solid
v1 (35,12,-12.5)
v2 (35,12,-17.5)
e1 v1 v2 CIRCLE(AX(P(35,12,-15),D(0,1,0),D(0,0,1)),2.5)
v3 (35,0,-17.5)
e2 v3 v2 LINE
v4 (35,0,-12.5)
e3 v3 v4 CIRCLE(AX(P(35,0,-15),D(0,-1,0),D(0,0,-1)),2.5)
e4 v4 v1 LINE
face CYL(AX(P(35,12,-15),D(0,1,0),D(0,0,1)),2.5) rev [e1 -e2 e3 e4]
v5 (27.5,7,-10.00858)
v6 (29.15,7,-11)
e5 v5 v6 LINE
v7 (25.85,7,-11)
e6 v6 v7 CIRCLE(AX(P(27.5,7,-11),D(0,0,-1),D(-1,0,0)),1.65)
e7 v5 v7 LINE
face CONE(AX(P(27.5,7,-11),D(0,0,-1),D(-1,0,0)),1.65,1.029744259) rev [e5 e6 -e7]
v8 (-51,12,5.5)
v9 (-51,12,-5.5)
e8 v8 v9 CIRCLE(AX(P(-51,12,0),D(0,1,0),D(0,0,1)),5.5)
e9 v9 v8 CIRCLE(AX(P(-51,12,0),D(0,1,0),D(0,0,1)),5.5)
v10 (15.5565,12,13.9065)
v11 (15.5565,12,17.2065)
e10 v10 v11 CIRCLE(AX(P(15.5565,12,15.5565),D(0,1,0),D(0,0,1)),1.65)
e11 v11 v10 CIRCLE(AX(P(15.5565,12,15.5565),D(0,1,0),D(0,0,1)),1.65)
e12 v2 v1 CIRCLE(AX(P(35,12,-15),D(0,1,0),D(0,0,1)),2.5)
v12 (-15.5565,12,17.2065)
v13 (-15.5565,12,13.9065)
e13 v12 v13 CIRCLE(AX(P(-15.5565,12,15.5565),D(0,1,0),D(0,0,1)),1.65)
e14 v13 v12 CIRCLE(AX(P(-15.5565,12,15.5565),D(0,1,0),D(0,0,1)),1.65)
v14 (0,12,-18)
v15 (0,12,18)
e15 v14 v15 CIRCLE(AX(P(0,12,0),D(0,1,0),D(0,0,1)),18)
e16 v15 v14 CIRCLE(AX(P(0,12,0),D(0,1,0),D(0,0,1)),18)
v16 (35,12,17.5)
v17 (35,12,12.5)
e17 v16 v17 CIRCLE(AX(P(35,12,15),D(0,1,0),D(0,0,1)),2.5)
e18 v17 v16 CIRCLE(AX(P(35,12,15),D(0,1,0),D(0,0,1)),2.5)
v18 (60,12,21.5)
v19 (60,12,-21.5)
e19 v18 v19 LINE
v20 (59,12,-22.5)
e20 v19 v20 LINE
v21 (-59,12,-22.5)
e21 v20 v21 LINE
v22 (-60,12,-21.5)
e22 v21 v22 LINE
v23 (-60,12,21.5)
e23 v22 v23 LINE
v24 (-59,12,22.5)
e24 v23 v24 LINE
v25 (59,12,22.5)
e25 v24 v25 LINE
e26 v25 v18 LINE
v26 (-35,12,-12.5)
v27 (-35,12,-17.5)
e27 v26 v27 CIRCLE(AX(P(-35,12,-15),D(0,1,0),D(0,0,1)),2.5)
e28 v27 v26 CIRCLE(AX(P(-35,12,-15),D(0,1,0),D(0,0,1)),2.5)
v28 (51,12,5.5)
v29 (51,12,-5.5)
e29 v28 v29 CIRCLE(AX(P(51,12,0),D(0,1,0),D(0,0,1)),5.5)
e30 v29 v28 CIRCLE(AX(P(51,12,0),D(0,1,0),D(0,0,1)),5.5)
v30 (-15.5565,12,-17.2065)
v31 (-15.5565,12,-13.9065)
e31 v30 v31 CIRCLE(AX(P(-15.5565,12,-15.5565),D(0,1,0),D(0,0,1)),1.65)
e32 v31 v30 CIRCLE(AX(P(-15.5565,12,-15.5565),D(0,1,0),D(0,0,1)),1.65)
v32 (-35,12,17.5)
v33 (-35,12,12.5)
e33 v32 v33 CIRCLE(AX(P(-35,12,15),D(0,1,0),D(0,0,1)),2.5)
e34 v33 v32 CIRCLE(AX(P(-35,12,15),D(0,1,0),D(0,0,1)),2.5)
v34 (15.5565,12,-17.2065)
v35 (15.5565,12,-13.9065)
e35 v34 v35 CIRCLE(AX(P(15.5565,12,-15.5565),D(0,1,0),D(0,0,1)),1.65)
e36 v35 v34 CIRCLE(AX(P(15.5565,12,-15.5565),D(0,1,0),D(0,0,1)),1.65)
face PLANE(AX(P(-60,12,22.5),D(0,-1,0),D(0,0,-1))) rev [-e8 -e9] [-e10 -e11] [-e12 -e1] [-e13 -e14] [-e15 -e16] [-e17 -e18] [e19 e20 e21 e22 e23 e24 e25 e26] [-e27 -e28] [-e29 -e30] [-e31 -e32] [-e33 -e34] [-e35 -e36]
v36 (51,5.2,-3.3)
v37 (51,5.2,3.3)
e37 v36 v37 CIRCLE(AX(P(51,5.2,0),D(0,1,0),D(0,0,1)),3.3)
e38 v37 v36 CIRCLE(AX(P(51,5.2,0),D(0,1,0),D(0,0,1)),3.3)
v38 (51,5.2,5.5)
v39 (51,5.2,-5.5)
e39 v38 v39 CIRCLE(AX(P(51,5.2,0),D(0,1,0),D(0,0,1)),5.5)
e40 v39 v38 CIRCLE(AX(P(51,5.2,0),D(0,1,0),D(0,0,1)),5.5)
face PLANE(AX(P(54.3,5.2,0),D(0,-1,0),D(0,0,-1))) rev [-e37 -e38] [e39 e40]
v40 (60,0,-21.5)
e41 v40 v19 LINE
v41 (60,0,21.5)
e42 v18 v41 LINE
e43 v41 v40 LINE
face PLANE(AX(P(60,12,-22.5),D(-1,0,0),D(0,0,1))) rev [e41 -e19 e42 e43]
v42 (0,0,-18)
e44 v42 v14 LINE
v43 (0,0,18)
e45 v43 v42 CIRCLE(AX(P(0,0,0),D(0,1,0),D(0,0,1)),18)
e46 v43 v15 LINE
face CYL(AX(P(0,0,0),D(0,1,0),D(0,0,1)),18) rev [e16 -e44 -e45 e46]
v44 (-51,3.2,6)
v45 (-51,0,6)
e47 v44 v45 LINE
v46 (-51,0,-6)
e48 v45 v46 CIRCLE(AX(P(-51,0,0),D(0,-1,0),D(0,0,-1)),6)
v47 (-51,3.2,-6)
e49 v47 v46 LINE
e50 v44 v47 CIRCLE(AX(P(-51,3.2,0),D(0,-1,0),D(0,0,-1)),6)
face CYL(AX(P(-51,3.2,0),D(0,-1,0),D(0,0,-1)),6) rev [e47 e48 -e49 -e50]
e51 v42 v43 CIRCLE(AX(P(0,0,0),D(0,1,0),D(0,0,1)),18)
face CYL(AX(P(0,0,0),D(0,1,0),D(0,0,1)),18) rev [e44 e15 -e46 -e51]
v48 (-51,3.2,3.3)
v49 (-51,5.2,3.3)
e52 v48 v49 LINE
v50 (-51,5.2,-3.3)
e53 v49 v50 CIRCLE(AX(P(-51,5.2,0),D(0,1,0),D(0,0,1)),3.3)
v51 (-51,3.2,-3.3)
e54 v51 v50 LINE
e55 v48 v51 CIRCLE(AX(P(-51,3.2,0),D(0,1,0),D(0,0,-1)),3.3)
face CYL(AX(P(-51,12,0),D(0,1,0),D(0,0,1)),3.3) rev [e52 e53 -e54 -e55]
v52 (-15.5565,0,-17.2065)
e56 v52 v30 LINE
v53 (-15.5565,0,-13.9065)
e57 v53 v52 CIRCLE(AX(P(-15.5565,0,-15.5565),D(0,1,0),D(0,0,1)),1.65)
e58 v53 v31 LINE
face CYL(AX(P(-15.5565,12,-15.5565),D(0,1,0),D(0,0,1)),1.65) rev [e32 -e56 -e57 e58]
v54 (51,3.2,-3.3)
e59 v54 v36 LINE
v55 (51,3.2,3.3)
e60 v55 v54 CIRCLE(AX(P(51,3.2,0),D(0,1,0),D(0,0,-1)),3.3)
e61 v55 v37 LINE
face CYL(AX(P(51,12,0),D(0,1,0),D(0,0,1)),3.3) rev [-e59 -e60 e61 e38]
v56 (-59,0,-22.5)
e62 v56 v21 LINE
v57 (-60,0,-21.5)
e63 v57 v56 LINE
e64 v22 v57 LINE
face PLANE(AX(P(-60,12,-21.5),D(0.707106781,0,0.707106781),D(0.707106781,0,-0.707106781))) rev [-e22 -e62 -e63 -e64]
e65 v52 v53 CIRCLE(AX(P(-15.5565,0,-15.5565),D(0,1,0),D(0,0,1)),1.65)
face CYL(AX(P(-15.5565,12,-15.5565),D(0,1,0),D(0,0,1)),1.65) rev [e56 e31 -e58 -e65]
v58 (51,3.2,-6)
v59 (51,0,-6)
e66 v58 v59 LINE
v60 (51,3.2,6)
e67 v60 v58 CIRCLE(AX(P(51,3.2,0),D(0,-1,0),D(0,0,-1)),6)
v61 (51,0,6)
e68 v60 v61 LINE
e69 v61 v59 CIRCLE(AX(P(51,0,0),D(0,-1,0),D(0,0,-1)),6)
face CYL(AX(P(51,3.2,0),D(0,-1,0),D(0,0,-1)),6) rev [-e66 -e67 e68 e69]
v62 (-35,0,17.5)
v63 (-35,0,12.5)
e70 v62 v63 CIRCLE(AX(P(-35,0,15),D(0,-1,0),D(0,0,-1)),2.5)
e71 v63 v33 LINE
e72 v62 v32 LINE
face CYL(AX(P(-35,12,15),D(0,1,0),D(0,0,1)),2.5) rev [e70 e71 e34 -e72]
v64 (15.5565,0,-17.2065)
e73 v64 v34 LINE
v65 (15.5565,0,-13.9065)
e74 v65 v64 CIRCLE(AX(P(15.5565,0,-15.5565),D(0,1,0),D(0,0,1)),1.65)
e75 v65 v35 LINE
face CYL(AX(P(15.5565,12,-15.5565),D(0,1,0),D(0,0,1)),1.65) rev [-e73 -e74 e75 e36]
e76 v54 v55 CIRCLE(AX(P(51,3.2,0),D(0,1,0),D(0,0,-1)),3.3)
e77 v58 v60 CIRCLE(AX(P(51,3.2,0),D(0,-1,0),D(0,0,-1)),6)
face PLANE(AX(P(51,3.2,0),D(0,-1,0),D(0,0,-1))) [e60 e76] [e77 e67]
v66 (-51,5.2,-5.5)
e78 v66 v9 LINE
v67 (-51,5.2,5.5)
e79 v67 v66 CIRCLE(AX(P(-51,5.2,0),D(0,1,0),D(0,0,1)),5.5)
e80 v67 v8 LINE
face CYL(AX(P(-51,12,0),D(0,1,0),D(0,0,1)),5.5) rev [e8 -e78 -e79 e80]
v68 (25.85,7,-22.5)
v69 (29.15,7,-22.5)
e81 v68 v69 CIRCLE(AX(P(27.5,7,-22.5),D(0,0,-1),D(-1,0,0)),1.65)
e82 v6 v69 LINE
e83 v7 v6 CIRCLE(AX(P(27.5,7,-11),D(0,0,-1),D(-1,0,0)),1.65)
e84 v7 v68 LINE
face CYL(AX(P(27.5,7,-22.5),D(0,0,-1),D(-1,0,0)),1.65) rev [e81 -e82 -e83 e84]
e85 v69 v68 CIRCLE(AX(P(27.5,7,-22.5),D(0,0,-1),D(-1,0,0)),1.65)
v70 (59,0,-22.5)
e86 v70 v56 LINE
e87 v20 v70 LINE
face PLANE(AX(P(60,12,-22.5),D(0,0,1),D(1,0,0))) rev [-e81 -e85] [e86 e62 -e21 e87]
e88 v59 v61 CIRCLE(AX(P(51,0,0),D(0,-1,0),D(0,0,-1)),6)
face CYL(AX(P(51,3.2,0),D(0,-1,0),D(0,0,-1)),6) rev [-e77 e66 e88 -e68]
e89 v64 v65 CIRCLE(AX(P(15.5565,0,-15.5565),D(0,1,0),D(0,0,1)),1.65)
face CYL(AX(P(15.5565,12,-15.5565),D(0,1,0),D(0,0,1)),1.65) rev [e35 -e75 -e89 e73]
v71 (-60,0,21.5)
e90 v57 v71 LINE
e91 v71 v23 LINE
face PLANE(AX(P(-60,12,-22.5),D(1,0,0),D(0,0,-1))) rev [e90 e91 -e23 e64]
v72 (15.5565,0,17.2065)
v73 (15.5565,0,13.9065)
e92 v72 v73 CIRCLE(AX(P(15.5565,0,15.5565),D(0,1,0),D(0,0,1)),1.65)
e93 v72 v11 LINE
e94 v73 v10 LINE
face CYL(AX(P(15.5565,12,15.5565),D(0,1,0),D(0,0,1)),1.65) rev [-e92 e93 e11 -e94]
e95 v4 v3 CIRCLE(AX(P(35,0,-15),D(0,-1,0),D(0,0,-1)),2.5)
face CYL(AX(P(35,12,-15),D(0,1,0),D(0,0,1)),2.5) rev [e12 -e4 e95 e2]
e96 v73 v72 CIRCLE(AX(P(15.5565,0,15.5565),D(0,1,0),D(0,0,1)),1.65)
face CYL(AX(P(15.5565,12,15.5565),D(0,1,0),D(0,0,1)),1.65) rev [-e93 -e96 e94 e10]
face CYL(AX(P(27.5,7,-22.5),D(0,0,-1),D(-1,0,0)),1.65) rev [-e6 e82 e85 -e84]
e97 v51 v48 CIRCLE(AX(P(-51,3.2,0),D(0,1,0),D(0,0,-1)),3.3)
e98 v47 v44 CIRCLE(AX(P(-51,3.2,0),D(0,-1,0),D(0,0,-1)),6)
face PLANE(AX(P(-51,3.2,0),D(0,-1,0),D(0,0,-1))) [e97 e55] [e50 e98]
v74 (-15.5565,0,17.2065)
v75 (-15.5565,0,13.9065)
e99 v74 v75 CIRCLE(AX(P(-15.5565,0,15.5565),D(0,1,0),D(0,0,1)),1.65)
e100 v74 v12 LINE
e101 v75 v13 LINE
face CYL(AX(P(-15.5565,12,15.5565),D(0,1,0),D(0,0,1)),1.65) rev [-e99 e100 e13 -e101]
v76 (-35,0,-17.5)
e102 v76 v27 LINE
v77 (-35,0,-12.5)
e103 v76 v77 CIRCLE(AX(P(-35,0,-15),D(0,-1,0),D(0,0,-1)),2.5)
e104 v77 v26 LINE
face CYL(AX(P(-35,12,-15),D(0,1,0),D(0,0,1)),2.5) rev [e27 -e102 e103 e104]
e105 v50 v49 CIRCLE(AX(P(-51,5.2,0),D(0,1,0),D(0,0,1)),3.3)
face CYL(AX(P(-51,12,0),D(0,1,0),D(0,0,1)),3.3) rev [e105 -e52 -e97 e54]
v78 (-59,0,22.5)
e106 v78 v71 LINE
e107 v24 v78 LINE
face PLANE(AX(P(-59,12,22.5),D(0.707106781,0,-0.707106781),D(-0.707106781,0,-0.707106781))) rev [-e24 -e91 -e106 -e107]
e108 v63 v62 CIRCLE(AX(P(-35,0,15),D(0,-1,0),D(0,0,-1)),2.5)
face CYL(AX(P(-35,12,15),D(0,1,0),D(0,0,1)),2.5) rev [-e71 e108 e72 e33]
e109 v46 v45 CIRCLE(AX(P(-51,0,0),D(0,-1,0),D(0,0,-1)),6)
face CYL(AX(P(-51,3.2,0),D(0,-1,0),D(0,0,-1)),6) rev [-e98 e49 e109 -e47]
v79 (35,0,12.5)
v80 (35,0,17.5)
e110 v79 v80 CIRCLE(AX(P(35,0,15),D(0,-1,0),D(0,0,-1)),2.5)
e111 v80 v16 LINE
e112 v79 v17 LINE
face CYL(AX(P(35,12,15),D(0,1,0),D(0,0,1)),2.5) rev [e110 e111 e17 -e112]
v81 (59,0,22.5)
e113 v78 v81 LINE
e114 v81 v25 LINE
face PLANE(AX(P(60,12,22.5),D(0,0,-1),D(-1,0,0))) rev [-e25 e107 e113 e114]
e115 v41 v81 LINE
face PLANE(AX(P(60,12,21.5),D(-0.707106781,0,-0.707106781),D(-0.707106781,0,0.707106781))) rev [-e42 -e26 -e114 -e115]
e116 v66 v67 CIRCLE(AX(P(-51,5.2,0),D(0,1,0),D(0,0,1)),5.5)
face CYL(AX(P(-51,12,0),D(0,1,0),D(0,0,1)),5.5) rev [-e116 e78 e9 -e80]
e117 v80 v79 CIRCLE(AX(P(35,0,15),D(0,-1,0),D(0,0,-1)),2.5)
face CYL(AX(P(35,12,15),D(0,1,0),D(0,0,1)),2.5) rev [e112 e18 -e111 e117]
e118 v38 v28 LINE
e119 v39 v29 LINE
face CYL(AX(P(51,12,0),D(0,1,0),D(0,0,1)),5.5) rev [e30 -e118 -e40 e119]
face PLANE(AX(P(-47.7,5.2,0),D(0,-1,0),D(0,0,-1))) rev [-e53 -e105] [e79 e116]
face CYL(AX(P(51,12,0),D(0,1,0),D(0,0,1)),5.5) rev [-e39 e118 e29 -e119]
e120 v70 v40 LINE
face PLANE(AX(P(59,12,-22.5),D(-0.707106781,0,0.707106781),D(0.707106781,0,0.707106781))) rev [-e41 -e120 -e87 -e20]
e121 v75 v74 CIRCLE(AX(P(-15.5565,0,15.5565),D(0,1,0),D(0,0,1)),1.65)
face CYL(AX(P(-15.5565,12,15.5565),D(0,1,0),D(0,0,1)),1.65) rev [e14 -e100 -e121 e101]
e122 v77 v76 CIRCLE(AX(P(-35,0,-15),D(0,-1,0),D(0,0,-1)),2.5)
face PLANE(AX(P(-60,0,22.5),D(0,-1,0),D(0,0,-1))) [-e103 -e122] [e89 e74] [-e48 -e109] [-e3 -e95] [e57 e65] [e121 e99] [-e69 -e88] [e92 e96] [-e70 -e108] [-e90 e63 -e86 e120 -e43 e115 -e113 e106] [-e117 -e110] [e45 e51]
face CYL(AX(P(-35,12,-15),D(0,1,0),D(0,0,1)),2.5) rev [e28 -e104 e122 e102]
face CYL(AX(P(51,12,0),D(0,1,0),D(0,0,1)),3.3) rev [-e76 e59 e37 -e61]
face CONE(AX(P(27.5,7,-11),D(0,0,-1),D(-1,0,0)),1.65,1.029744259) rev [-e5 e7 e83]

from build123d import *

# Parameters (mm, degrees)
SKETCH1_W                                            = 120
SKETCH1_H                                            = 45
BOSS_EXTRUDE1_DEPTH                                  = 12
CHAMFER1_SIZE                                        = 1
SKETCH2_R                                            = 18
CUT_EXTRUDE1_DEPTH                                   = 66.193941436
M4_TAPPED_HOLE1_D                                    = 3.3
HOLE_SIZE_PER_SOCKET_HEAD_CAP_SCREW_TYPE_D           = 6.6
HOLE_SIZE_PER_SOCKET_HEAD_CAP_SCREW_TYPE_CBORE_D     = 11
HOLE_SIZE_PER_SOCKET_HEAD_CAP_SCREW_TYPE_CBORE_DEPTH = 6.8
SKETCH7_R                                            = 6
CUT_EXTRUDE2_DEPTH                                   = 3.2
M4_TAPPED_HOLE2_D                                    = 3.3
M4_TAPPED_HOLE2_DEPTH                                = 11.5
M4_TAPPED_HOLE2_TIP                                  = 0.991420021
M6_TAPPED_HOLE1_D                                    = 5


with BuildPart() as part:
    # Sketch1 → Boss-Extrude1 (new body)
    with BuildSketch(Plane(origin=(0, 0, 0), x_dir=(1, 0, 0), z_dir=(0, 1, 0))):
        Rectangle(SKETCH1_W, SKETCH1_H)
    extrude(amount=BOSS_EXTRUDE1_DEPTH)

    # Chamfer1
    chamfer1_edges = [part.edges().sort_by_distance(p)[0] for p in [
        (-60, 6, -22.5),
        (60, 6, -22.5),
        (60, 6, 22.5),
        (-60, 6, 22.5),
    ]]
    chamfer(chamfer1_edges, length=CHAMFER1_SIZE)

    # Sketch2 → Cut-Extrude1 (cut, through all)
    with BuildSketch(Plane(origin=(0, 12, 0), x_dir=(1, 0, 0), z_dir=(0, 1, 0))):
        with Locations(Location((0, 0, 0), (0, 0, 270))):
            Circle(SKETCH2_R)
    extrude(amount=-CUT_EXTRUDE1_DEPTH, mode=Mode.SUBTRACT)

    # M4 Tapped Hole1 (through all)
    with Locations(Plane(origin=(0, 12, 0), x_dir=(-1, 0, 0), z_dir=(0, 1, 0))):
        with Locations((15.5565, -15.5565), (15.5565, 15.5565), (-15.5565, 15.5565), (-15.5565, -15.5565)):
            Hole(M4_TAPPED_HOLE1_D / 2)

    # Hole size per socket head cap screw type1 (through all)
    with Locations(Plane(origin=(0, 12, 0), x_dir=(-1, 0, 0), z_dir=(0, 1, 0))):
        with Locations((51, 0), (-51, 0)):
            CounterBoreHole(HOLE_SIZE_PER_SOCKET_HEAD_CAP_SCREW_TYPE_D / 2, HOLE_SIZE_PER_SOCKET_HEAD_CAP_SCREW_TYPE_CBORE_D / 2, HOLE_SIZE_PER_SOCKET_HEAD_CAP_SCREW_TYPE_CBORE_DEPTH)

    # Sketch7 → Cut-Extrude2 (cut)
    with BuildSketch(Plane.XZ):
        with Locations(Location((51, 0, 0), (0, 0, 270))):
            Circle(SKETCH7_R)
        with Locations(Location((-51, 0, 0), (0, 0, 270))):
            Circle(SKETCH7_R)
    extrude(amount=-CUT_EXTRUDE2_DEPTH, mode=Mode.SUBTRACT)

    # M4 Tapped Hole2
    with Locations(Plane(origin=(0, 0, -22.5), x_dir=(-1, 0, 0), z_dir=(0, 0, -1))):
        with Locations((-27.5, 7)):
            Hole(M4_TAPPED_HOLE2_D / 2, depth=M4_TAPPED_HOLE2_DEPTH)
            with Locations((0, 0, -(M4_TAPPED_HOLE2_DEPTH + M4_TAPPED_HOLE2_TIP / 2))):  # 118° drill point
                Cone(0, M4_TAPPED_HOLE2_D / 2, M4_TAPPED_HOLE2_TIP, mode=Mode.SUBTRACT)

    # M6 Tapped Hole1 (through all)
    with Locations(Plane(origin=(0, 12, 0), x_dir=(1, 0, 0), z_dir=(0, 1, 0))):
        with Locations((35, -15), (35, 15), (-35, -15), (-35, 15)):
            Hole(M6_TAPPED_HOLE1_D / 2)


solid = part.part
